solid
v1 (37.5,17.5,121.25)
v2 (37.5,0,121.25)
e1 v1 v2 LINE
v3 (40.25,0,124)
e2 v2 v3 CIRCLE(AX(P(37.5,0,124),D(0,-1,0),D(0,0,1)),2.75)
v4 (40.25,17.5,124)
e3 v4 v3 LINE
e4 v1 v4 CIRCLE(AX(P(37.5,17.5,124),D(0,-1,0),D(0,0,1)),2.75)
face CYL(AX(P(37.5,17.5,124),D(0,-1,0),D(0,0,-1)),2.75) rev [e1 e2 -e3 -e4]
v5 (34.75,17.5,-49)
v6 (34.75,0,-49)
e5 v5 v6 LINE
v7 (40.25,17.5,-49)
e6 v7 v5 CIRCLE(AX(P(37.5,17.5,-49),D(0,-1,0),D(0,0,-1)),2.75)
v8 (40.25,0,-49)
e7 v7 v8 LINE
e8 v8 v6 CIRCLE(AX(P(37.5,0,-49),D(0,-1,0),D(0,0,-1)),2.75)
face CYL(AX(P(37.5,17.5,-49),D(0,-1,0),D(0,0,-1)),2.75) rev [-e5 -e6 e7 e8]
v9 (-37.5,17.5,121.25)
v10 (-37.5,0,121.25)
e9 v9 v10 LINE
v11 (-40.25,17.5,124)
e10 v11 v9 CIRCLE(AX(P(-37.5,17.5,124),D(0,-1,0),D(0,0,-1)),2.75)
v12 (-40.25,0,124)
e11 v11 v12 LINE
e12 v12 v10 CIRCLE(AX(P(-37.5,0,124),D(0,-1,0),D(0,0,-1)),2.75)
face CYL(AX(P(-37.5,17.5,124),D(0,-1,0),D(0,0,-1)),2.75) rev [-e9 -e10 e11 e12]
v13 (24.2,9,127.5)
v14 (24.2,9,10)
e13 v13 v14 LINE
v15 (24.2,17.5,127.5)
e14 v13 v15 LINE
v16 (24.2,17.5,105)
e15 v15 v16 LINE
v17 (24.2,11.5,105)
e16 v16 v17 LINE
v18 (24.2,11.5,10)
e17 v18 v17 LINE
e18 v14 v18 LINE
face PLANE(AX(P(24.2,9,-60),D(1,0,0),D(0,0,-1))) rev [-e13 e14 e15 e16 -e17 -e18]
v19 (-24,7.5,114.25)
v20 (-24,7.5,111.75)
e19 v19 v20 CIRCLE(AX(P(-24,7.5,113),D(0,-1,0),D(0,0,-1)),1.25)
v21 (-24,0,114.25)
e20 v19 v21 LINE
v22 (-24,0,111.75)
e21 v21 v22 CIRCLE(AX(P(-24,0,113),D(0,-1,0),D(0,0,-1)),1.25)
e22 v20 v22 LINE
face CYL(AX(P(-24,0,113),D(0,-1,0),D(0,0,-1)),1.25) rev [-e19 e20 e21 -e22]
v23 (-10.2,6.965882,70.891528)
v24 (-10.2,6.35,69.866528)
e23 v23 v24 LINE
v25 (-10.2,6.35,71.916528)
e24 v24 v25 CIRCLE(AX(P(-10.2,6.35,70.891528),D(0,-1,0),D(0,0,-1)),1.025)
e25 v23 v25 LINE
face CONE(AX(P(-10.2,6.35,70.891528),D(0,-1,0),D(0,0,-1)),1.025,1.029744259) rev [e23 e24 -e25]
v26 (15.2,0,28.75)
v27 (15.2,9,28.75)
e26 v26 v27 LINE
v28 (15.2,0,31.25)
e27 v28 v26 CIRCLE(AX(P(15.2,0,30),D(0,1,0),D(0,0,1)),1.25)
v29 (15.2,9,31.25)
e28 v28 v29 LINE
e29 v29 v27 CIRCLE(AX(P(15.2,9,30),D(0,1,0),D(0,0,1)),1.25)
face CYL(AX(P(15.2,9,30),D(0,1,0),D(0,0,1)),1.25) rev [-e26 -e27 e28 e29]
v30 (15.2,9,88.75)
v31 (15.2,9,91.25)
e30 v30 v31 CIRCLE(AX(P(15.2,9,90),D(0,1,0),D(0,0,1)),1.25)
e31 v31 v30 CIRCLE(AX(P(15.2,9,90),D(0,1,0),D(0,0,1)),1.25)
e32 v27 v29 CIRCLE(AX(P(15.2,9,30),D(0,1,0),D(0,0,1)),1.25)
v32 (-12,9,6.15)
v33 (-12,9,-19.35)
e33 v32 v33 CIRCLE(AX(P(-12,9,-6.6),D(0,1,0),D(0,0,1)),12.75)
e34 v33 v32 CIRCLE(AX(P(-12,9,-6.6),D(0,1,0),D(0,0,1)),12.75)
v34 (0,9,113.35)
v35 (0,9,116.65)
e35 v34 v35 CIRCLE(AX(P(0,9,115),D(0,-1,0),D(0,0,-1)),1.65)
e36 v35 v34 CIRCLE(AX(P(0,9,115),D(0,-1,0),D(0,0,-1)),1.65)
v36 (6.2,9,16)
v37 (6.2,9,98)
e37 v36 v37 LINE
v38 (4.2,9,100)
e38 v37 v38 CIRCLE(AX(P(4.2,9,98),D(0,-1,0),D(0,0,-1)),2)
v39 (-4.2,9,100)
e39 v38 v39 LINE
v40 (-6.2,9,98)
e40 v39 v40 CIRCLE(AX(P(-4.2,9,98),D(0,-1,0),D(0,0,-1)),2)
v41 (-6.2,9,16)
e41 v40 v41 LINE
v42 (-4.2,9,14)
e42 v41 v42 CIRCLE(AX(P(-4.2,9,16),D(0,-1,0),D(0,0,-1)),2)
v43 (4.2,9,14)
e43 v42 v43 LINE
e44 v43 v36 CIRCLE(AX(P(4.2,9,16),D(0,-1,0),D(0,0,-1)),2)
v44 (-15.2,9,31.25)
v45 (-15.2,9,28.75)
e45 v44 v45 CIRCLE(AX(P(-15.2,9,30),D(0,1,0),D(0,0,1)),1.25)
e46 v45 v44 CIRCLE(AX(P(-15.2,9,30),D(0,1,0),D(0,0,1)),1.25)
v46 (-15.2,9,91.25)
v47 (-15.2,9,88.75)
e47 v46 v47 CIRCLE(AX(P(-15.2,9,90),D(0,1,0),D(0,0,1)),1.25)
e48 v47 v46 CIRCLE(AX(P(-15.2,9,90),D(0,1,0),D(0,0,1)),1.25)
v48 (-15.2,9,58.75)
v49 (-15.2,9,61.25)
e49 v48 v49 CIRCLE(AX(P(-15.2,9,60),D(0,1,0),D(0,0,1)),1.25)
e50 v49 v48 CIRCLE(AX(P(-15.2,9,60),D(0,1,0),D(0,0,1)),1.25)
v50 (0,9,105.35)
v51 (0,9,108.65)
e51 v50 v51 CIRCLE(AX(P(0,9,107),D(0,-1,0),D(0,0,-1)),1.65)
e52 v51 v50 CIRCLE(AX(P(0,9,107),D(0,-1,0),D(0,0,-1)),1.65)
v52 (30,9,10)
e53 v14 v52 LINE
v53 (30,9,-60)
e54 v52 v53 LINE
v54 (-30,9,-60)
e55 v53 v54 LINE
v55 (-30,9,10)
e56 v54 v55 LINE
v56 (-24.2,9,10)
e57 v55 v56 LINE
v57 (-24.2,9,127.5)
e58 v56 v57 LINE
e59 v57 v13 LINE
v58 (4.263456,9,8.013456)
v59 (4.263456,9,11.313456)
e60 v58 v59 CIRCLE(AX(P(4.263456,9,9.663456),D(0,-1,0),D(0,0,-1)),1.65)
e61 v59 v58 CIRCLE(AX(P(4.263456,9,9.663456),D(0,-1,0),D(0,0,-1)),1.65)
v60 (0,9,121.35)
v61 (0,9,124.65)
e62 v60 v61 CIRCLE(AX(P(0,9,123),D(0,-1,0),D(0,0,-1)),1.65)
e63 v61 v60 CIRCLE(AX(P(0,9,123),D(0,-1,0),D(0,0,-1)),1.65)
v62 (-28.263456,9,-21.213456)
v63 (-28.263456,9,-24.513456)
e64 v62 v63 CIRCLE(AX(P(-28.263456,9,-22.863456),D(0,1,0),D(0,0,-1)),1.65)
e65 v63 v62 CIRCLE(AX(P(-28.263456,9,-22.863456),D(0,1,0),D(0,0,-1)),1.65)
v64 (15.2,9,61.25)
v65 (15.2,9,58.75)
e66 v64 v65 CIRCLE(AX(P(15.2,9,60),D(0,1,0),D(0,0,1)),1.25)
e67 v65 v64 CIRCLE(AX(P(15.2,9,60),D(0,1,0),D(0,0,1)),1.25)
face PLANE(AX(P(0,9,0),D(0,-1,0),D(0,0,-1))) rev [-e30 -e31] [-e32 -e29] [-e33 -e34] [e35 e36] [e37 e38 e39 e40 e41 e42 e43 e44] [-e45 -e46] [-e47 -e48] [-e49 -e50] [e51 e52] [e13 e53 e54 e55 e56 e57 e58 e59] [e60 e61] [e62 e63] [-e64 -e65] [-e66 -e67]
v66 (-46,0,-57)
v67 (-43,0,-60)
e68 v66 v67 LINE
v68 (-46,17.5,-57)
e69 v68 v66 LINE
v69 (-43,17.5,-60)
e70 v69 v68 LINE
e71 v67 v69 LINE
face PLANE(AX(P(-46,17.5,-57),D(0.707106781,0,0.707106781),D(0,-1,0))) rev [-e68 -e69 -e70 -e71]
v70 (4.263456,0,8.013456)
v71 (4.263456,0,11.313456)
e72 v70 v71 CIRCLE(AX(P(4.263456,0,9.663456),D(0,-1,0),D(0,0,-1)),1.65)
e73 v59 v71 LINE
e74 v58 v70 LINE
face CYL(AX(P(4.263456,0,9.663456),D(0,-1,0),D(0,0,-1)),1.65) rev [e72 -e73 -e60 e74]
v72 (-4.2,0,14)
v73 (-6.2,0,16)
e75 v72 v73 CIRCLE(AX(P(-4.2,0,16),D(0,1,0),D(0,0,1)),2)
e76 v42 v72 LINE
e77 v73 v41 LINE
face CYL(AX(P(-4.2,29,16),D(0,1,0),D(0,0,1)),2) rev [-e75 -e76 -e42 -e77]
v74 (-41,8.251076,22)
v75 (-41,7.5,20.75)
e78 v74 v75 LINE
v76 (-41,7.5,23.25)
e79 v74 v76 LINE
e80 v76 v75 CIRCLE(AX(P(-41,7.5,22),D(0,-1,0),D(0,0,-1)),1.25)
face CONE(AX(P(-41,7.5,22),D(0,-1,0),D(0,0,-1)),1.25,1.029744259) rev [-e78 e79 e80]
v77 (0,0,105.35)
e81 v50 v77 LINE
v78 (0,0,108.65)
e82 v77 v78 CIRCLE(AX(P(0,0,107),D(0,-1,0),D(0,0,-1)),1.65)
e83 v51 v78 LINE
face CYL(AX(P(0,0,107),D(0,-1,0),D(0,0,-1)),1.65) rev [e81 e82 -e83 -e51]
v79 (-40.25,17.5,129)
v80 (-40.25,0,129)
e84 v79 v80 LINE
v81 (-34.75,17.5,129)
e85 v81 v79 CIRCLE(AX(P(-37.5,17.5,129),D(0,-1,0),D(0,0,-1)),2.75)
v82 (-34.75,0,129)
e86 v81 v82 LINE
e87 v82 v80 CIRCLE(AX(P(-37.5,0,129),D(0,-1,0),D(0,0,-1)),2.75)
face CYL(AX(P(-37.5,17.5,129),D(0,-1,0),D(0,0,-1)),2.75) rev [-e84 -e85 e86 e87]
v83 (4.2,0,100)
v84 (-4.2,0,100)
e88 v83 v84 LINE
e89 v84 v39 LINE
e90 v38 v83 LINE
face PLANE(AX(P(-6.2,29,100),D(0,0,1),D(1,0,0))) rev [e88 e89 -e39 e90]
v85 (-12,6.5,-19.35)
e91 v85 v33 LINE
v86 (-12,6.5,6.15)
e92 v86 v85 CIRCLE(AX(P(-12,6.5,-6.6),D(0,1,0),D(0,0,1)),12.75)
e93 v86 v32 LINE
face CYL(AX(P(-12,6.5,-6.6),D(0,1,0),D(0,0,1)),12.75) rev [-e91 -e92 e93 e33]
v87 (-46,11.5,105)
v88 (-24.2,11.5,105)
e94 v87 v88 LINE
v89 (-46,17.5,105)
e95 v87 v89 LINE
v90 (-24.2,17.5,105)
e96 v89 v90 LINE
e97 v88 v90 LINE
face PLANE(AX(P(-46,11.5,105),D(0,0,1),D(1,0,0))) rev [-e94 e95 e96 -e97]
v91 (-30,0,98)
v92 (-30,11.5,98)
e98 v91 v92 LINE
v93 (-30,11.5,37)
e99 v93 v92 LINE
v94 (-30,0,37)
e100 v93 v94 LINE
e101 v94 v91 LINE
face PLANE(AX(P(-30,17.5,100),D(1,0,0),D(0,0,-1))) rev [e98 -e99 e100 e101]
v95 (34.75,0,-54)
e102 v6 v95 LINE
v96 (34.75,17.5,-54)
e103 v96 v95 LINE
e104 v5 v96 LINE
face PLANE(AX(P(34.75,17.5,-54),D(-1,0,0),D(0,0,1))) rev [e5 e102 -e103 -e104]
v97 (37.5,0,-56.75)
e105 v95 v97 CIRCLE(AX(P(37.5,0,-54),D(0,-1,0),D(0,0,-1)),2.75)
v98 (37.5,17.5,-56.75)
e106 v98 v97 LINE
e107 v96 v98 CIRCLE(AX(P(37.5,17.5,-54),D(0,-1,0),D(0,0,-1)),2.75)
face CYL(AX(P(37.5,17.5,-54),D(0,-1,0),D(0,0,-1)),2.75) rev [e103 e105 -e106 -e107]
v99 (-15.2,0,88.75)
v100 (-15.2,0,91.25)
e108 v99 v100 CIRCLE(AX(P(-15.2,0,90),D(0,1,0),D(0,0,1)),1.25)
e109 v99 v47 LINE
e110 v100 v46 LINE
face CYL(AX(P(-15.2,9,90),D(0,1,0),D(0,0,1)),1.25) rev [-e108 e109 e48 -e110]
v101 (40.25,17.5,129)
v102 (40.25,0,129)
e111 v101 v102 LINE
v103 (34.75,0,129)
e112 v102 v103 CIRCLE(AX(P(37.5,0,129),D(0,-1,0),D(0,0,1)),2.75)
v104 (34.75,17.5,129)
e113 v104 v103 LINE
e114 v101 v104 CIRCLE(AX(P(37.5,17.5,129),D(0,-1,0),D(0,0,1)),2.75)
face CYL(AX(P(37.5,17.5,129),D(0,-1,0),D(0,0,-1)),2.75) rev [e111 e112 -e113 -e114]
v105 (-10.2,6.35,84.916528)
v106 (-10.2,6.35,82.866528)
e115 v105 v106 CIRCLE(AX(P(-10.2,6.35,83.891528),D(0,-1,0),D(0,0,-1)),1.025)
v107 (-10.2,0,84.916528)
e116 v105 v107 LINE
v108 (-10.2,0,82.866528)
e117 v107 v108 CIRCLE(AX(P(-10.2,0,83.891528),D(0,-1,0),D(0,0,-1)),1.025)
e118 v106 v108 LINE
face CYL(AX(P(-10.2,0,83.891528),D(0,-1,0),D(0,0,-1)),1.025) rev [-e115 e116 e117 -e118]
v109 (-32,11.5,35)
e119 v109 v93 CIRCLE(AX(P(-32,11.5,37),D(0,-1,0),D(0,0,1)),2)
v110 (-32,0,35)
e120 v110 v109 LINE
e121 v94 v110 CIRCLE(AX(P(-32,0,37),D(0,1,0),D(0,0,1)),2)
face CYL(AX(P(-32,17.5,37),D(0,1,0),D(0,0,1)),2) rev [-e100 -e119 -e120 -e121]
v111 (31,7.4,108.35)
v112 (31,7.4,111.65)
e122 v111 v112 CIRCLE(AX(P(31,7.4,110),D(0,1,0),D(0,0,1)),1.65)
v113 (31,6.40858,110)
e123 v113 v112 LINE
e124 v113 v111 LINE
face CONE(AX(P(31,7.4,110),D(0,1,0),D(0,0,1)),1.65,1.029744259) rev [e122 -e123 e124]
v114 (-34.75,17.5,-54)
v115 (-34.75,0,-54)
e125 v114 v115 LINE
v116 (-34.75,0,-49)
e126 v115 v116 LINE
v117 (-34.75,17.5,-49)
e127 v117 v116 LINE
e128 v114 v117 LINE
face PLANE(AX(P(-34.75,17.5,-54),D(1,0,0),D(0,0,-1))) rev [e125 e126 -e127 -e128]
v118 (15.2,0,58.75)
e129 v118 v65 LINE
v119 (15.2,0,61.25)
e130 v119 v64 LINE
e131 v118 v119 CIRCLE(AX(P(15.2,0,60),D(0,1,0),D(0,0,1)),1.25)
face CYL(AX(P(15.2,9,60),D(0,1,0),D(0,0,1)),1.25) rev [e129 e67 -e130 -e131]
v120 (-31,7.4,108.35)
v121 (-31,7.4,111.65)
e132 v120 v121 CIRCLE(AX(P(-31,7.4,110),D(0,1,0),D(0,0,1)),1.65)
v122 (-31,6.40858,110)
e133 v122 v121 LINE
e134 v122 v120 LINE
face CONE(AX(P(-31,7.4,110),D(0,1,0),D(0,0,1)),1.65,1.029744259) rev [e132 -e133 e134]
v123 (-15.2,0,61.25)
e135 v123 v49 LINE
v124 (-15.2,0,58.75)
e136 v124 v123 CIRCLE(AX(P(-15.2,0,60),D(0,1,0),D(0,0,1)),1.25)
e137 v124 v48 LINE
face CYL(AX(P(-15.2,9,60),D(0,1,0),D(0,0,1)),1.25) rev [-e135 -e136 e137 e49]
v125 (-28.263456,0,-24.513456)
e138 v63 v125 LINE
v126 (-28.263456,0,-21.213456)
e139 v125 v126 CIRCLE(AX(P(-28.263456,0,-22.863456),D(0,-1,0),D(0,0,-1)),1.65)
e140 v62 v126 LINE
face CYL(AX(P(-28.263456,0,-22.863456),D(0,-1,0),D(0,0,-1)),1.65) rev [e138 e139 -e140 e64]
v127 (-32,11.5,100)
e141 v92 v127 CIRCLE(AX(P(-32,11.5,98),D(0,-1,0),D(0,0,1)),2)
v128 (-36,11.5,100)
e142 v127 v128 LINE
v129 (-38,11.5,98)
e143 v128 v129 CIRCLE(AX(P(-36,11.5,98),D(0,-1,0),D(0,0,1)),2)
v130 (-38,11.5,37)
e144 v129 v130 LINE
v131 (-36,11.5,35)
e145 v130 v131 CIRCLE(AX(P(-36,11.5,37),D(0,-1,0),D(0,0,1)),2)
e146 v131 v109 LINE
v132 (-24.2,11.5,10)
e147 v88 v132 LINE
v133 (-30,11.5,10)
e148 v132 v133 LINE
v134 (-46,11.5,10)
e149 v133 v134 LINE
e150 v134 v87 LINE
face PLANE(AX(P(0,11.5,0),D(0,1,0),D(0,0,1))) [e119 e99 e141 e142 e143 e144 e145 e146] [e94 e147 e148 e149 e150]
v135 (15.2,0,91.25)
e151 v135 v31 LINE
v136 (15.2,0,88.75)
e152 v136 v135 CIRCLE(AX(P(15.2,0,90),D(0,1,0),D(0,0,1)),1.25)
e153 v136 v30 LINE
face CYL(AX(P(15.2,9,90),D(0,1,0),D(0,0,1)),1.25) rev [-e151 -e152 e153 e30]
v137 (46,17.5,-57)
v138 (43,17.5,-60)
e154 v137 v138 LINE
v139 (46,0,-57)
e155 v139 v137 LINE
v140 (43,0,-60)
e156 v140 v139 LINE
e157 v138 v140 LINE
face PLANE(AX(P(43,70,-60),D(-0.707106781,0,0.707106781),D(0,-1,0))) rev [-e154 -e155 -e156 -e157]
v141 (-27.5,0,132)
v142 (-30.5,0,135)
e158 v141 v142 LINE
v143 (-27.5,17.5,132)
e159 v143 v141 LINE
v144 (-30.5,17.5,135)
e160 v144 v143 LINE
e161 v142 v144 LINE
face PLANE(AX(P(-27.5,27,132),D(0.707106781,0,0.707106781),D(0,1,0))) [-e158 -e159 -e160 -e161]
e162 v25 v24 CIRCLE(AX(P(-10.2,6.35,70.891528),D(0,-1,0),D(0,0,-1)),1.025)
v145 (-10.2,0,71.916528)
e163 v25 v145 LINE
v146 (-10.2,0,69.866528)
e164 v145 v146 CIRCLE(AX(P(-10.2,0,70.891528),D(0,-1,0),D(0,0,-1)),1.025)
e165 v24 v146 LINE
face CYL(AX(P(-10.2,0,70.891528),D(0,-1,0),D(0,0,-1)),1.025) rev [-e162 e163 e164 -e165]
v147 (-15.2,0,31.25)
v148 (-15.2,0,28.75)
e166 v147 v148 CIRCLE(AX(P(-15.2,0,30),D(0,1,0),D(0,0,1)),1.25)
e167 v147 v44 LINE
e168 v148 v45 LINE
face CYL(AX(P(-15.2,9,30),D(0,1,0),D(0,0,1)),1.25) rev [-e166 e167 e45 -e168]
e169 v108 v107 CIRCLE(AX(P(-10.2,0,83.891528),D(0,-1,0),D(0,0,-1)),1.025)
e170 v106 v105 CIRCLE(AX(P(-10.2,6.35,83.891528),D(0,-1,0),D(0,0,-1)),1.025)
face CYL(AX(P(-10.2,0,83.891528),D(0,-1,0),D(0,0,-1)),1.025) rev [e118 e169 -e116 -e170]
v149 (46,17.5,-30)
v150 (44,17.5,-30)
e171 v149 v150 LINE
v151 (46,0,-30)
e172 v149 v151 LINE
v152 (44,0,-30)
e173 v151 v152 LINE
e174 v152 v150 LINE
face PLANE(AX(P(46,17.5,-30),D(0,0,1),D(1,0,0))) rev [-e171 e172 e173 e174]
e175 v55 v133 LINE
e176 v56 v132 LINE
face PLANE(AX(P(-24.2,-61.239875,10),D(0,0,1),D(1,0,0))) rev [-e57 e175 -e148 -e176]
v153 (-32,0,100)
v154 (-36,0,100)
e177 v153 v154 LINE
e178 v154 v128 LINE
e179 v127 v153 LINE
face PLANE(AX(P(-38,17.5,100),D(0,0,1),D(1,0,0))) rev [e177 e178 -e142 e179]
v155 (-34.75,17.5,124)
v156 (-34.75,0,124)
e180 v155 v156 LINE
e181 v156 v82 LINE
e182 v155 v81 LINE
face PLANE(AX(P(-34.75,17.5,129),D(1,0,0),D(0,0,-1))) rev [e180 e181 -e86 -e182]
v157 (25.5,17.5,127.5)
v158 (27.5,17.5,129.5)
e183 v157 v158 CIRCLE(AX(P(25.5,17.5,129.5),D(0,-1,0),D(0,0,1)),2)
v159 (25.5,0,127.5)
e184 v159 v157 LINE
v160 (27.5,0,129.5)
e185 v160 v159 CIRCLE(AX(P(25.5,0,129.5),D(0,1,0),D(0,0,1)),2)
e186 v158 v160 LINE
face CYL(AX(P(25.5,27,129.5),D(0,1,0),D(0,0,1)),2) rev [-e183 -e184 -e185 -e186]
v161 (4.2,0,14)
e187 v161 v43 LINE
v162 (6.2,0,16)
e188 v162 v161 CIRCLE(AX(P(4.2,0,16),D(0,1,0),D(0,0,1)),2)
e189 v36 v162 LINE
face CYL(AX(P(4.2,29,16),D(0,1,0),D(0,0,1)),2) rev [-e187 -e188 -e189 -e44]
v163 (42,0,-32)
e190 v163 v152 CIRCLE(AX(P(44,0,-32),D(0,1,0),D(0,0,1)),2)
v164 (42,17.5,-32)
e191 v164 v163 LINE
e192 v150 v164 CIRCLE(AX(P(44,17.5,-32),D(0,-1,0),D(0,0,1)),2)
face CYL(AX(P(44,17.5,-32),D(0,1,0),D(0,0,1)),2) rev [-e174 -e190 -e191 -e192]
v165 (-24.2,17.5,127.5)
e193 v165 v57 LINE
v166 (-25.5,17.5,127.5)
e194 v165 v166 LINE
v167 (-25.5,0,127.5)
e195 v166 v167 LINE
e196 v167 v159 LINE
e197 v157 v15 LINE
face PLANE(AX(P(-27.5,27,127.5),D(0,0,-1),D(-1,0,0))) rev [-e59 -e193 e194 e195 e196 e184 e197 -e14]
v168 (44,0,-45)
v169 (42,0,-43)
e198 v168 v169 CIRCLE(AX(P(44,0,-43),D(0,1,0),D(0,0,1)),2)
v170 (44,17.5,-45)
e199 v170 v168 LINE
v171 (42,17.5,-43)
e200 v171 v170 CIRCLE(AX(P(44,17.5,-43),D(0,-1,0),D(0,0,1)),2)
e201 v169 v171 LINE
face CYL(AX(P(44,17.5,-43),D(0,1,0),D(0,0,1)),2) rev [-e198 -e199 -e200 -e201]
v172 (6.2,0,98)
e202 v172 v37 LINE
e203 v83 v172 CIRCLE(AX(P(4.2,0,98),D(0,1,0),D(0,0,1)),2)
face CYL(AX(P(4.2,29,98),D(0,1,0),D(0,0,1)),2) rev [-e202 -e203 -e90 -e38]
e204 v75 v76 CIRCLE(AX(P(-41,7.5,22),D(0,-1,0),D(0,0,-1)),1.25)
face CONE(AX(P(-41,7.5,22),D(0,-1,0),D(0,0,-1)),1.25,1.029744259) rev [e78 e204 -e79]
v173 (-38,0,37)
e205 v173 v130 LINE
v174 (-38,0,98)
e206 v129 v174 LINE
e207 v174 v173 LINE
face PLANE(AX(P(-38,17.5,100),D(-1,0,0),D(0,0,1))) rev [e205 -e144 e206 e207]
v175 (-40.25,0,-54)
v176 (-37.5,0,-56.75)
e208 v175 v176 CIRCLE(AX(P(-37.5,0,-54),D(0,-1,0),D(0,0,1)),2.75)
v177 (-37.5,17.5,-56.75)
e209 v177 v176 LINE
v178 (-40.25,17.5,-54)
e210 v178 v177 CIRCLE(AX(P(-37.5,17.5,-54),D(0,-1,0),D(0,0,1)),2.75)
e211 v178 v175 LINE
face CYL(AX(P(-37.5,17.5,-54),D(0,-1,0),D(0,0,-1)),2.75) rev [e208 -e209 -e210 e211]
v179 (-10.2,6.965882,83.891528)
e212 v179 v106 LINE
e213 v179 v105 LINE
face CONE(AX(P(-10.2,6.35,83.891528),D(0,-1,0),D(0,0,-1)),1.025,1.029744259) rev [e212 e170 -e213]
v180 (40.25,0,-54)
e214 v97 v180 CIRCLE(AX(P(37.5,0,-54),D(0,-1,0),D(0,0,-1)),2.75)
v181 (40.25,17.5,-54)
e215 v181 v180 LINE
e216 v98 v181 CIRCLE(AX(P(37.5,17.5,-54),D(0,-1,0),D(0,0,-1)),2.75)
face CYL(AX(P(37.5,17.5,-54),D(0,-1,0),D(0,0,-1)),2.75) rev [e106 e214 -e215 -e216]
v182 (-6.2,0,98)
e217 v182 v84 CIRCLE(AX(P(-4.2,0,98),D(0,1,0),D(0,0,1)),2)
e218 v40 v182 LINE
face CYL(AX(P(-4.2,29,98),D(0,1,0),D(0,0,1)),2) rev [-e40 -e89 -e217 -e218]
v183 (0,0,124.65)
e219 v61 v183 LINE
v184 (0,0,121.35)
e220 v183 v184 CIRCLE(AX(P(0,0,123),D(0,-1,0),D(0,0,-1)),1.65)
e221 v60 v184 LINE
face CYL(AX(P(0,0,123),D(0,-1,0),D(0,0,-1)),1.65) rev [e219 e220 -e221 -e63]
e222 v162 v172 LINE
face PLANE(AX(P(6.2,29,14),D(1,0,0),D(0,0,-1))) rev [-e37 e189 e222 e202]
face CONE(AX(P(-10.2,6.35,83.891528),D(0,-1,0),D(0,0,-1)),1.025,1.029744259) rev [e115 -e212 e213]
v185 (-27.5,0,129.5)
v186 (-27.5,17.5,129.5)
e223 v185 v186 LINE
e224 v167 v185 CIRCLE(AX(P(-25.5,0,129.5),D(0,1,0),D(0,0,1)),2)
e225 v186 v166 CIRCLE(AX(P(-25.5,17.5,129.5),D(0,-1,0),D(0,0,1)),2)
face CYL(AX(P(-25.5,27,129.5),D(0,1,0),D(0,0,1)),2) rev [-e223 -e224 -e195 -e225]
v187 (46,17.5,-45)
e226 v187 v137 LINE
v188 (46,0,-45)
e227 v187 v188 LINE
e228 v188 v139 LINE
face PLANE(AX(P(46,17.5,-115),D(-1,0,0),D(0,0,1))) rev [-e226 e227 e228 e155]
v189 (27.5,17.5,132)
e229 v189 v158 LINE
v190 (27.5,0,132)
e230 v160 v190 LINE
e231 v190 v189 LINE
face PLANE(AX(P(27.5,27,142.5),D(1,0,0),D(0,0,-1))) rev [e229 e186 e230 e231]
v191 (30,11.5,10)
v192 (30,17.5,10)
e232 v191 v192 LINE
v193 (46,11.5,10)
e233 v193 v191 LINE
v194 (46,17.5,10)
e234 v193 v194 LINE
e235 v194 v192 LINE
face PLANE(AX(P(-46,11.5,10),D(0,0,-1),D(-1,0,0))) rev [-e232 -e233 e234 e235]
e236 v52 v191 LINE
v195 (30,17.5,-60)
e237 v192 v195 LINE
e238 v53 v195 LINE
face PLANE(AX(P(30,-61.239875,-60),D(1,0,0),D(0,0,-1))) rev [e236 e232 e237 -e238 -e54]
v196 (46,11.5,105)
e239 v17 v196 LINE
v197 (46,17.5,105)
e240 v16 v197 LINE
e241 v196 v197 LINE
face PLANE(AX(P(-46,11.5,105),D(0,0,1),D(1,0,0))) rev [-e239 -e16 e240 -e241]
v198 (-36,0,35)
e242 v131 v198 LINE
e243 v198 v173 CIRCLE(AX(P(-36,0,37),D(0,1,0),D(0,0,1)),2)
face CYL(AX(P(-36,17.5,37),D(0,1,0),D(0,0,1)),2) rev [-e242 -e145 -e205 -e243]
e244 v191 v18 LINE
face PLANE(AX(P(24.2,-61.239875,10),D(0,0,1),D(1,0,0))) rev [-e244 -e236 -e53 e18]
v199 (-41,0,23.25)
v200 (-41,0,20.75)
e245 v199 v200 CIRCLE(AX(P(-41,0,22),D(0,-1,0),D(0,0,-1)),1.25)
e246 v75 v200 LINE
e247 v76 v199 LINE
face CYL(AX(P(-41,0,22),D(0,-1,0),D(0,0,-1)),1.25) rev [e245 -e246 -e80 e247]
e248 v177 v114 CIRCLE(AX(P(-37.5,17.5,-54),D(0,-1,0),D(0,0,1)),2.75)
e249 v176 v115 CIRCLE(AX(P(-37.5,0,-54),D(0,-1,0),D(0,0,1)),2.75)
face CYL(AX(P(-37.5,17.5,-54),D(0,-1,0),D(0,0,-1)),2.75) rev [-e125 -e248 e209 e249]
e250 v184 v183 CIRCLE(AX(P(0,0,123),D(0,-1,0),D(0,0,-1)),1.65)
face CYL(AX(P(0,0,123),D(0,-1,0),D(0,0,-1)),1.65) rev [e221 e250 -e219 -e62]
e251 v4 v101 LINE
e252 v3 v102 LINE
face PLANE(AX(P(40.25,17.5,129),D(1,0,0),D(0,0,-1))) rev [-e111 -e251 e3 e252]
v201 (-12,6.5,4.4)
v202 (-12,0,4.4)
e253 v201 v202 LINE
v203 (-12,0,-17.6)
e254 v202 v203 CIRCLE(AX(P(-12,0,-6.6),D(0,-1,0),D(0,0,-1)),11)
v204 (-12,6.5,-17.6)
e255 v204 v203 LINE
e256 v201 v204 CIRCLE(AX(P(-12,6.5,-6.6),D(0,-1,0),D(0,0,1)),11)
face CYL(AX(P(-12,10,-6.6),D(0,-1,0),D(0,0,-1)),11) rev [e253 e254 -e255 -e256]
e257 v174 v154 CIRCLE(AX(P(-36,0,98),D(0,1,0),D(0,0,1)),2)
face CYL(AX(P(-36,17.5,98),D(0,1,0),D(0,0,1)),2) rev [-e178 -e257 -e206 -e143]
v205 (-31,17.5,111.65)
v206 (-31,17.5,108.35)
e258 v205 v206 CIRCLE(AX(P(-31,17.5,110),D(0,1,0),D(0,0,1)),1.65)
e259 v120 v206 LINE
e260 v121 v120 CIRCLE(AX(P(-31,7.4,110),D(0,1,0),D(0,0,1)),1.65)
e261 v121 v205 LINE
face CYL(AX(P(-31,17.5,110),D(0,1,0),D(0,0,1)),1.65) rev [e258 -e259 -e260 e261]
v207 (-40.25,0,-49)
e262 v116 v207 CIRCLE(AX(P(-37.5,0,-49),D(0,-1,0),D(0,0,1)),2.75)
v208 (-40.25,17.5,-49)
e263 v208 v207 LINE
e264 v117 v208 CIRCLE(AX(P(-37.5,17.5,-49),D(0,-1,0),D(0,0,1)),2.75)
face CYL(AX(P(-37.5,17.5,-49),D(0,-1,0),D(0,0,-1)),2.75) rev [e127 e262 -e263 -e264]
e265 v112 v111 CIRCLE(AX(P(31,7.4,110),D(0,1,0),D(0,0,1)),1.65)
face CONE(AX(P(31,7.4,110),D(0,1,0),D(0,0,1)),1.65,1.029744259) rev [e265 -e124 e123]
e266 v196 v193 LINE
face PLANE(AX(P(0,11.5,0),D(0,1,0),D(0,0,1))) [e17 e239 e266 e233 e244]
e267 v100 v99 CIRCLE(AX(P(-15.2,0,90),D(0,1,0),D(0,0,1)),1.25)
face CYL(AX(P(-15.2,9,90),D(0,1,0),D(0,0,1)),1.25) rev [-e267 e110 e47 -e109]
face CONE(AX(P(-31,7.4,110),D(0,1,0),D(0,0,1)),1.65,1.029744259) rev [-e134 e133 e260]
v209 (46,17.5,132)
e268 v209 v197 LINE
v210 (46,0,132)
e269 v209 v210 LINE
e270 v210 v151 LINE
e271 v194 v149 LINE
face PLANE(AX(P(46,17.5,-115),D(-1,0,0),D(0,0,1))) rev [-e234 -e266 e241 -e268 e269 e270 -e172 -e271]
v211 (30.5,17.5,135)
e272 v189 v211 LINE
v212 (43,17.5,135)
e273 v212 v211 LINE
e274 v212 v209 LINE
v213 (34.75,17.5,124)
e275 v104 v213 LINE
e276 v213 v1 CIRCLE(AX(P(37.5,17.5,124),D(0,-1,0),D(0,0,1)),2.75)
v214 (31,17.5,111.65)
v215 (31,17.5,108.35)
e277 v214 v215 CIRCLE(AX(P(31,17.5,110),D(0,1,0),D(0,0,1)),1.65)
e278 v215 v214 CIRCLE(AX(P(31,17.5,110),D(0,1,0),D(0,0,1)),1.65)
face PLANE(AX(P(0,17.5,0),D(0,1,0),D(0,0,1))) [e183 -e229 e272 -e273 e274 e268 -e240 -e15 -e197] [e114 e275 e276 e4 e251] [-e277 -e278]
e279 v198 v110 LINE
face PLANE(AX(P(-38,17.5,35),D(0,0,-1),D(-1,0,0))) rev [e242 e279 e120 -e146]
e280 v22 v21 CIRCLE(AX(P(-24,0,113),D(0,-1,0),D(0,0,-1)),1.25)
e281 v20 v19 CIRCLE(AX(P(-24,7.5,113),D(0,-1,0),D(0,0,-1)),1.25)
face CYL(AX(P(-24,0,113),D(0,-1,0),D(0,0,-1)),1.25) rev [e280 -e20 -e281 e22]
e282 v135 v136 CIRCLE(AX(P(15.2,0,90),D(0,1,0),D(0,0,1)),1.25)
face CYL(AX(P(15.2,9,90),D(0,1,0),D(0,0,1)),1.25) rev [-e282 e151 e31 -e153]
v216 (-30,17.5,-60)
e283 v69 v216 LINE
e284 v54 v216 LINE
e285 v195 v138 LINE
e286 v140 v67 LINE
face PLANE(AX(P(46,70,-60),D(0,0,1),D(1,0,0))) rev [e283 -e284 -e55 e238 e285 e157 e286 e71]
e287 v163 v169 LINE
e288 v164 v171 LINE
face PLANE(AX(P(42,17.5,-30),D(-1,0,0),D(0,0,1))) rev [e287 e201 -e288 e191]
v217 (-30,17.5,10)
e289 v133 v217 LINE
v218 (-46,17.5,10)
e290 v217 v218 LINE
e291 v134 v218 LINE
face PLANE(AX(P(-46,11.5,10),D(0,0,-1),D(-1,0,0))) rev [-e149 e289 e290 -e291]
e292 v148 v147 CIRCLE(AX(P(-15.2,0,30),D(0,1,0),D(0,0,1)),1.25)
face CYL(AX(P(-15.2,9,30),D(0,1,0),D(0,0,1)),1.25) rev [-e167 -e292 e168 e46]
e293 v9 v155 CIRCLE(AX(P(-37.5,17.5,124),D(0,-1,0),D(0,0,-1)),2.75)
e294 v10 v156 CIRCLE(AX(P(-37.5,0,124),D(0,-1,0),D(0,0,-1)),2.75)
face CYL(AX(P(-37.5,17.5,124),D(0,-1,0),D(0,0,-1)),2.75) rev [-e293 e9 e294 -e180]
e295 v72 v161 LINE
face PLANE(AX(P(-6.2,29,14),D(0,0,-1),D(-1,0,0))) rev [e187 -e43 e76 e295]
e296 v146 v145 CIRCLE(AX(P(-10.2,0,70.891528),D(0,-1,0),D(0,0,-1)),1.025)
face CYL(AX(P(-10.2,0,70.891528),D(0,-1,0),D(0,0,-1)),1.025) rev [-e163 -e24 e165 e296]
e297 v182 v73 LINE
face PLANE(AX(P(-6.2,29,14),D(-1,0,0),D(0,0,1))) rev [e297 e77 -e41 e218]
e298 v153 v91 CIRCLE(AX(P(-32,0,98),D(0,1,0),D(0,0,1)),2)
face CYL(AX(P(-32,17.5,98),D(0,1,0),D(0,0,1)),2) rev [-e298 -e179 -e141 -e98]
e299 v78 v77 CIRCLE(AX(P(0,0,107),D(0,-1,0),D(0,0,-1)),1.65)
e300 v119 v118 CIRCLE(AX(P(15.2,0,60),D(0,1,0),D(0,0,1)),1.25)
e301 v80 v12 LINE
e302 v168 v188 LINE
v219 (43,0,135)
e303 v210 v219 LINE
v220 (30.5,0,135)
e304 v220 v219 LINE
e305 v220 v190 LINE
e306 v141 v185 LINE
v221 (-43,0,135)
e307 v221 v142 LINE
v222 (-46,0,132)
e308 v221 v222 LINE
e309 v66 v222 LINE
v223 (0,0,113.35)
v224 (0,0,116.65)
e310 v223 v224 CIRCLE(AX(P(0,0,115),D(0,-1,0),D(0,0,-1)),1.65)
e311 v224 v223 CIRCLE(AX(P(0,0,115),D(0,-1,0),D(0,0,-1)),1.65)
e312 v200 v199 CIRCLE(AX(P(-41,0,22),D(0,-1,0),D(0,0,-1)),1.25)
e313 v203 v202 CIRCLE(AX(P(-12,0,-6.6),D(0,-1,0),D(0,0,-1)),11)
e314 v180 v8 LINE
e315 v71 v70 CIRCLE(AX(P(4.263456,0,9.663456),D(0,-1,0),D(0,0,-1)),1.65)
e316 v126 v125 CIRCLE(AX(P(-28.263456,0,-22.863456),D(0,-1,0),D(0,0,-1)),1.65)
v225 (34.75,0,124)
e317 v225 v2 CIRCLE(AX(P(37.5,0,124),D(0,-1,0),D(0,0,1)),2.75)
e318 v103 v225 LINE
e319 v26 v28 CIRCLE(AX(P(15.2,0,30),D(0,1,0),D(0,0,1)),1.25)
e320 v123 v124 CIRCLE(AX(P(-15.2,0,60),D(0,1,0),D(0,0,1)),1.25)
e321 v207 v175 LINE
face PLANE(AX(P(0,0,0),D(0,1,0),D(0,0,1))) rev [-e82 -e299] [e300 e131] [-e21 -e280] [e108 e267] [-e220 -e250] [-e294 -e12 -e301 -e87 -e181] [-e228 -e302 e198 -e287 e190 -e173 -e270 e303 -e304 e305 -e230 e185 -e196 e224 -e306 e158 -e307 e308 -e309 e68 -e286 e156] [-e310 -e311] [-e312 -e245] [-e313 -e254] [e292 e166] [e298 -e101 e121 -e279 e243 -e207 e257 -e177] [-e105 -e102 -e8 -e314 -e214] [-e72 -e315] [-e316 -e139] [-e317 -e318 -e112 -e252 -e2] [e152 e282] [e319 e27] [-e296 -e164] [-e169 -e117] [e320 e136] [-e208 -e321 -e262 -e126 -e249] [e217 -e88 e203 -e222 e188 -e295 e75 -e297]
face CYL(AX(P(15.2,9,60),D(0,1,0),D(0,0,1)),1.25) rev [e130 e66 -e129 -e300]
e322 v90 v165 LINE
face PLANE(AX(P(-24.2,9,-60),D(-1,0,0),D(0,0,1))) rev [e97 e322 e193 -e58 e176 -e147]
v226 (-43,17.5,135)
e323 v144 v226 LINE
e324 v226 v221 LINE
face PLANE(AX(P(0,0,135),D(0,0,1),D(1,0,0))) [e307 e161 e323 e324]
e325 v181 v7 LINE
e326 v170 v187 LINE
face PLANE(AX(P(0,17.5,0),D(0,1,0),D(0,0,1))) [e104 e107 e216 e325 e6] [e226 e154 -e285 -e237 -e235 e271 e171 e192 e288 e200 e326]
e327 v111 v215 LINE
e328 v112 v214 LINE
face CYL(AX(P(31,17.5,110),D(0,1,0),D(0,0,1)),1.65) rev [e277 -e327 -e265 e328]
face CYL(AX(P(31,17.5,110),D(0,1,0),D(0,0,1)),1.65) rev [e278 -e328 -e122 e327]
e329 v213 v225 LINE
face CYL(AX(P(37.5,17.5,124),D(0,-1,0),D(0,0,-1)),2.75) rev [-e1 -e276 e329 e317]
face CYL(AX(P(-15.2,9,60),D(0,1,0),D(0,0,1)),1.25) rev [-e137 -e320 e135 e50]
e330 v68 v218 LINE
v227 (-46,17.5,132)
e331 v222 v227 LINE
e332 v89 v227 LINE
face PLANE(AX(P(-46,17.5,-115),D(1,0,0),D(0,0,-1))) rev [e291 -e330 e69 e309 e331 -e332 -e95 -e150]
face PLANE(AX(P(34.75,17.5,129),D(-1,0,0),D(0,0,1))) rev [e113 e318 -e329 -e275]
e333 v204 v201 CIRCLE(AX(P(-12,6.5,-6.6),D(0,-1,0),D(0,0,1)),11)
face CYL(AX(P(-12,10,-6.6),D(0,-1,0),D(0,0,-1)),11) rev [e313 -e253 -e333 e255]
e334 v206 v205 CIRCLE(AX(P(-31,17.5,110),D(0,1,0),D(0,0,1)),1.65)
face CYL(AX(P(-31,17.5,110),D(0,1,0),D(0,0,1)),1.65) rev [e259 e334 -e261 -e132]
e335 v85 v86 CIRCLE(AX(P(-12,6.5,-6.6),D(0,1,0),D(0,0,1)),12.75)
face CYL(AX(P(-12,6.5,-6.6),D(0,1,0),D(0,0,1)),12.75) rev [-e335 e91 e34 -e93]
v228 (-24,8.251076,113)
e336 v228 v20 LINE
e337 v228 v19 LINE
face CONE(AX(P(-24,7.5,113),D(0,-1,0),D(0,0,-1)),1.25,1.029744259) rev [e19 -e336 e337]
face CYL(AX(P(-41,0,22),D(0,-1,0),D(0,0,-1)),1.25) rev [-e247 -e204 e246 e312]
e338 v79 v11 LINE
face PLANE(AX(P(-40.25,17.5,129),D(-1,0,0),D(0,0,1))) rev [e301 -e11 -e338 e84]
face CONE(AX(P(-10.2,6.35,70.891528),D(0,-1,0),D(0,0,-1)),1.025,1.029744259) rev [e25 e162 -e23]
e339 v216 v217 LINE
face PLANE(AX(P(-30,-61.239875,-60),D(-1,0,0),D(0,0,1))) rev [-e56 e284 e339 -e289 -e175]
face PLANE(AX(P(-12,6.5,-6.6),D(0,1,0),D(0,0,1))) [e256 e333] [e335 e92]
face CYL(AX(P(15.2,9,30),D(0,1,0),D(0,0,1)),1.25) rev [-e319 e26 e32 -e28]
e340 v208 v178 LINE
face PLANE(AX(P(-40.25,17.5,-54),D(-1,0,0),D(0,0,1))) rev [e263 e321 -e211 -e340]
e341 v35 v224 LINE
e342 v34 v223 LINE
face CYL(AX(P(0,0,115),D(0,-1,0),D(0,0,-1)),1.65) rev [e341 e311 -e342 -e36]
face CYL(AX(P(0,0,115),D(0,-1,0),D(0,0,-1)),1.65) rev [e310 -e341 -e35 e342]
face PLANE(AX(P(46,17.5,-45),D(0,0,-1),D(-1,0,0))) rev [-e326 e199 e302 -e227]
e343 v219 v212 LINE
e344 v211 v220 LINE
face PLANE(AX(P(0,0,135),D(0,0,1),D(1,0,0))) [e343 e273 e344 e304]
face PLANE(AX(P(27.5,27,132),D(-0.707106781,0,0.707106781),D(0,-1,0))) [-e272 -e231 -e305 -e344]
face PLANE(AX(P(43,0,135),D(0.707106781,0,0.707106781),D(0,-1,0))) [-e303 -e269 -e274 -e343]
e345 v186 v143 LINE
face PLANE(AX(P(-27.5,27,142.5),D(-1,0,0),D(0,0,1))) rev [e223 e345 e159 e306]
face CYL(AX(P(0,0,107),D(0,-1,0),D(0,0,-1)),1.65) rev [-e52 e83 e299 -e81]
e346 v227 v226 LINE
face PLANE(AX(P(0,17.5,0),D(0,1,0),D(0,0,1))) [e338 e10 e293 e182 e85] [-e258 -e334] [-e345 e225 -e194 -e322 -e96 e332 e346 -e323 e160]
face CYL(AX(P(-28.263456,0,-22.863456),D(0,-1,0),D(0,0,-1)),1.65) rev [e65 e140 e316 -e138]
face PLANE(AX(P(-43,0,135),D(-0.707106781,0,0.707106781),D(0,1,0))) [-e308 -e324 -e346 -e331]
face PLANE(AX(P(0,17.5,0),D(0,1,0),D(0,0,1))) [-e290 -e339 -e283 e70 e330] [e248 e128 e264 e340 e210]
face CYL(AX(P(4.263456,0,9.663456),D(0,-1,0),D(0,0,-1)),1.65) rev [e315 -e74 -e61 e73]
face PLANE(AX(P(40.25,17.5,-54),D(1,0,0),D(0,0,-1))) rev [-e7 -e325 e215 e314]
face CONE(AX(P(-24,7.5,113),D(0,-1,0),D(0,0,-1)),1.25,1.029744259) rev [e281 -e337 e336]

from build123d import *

# Parameters (mm, degrees)
SKETCH1_W               = 92
SKETCH1_H               = 230
BOSS_EXTRUDE1_DEPTH     = 17.5
SKETCH3_W               = 92
SKETCH3_H               = 20
CUT_EXTRUDE2_DEPTH      = 57
SKETCH7_W               = 92
SKETCH7_H               = 35
CUT_EXTRUDE5_DEPTH      = 70
SKETCH6_W               = 48.4
SKETCH6_H               = 175
CUT_EXTRUDE4_DEPTH      = 8.5
M3_TAPPED_HOLE1_D       = 2.5
SKETCH4_W               = 12.4
SKETCH4_H               = 86
CUT_EXTRUDE3_DEPTH      = 29
CHAMFER1_SIZE           = 3
FILLET1_R               = 2
SKETCH2_R               = 11
CUT_EXTRUDE1_DEPTH      = 10
BOSS_EXTRUDE2_DEPTH     = 20
CUT_EXTRUDE9_DEPTH      = 144.69150984
CHAMFER2_SIZE           = 3
SKETCH22_W              = 8
SKETCH22_H              = 65
CUT_EXTRUDE10_DEPTH     = 144.69150984
FILLET2_R               = 2
SKETCH12_R              = 12.75
CUT_EXTRUDE7_DEPTH      = 2.5
SKETCH23_W              = 92
SKETCH23_H              = 95
CUT_EXTRUDE11_DEPTH     = 6
M2_5_TAPPED_HOLE1_D     = 2.05
M2_5_TAPPED_HOLE1_DEPTH = 6.35
M2_5_TAPPED_HOLE1_TIP   = 0.615882135
M4_TAPPED_HOLE4_D       = 3.3
M4_TAPPED_HOLE4_DEPTH   = 10.1
M4_TAPPED_HOLE4_TIP     = 0.991420021
SKETCH16_R              = 1
CUT_EXTRUDE8_DEPTH      = 10
SKETCH30_W              = 4
SKETCH30_H              = 15
CUT_EXTRUDE12_DEPTH     = 144.69150984
M4_TAPPED_HOLE2_D       = 3.3
FILLET3_R               = 2
LPATTERN1_COUNT         = 3
LPATTERN1_PITCH         = 8
SKETCH31_W              = 55
SKETCH31_H              = 15
CUT_EXTRUDE13_DEPTH     = 27
FILLET4_R               = 2
CHAMFER3_SIZE           = 3
CUT_EXTRUDE14_REACH     = 145.692
SKETCH32_W              = 5.8
SKETCH32_H              = 70
M3_TAPPED_HOLE2_D       = 2.5
M3_TAPPED_HOLE2_DEPTH   = 7.5
M3_TAPPED_HOLE2_TIP     = 0.751075774
M3_TAPPED_HOLE3_D       = 2.5
M3_TAPPED_HOLE3_DEPTH   = 7.5
M3_TAPPED_HOLE3_TIP     = 0.751075774


with BuildPart() as part:
    # Sketch1 → Boss-Extrude1 (new body)
    with BuildSketch(Plane(origin=(0, 0, 0), x_dir=(1, 0, 0), z_dir=(0, 1, 0))):
        Rectangle(SKETCH1_W, SKETCH1_H)
    extrude(amount=BOSS_EXTRUDE1_DEPTH)

    # Sketch3 → Cut-Extrude2 (cut)
    with BuildSketch(Plane.XZ):
        with Locations((0, -105)):
            Rectangle(SKETCH3_W, SKETCH3_H)
    extrude(amount=-CUT_EXTRUDE2_DEPTH, mode=Mode.SUBTRACT)

    # Sketch7 → Cut-Extrude5 (cut)
    with BuildSketch(Plane.XZ):
        with Locations((0, -77.5)):
            Rectangle(SKETCH7_W, SKETCH7_H)
    extrude(amount=-CUT_EXTRUDE5_DEPTH, mode=Mode.SUBTRACT)

    # Sketch6 → Cut-Extrude4 (cut)
    with BuildSketch(Plane(origin=(0, 17.5, 0), x_dir=(1, 0, 0), z_dir=(0, 1, 0))):
        with Locations((0, -27.5)):
            Rectangle(SKETCH6_W, SKETCH6_H)
    extrude(amount=-CUT_EXTRUDE4_DEPTH, mode=Mode.SUBTRACT)

    # M3 Tapped Hole1 (through all)
    with Locations(Plane(origin=(0, 9, 0), x_dir=(1, 0, 0), z_dir=(0, 1, 0))):
        with Locations((15.2, -90), (-15.2, -90), (-15.2, -60), (15.2, -60), (15.2, -30), (-15.2, -30)):
            Hole(M3_TAPPED_HOLE1_D / 2)

    # Sketch4 → Cut-Extrude3 (cut)
    with BuildSketch(Plane.XZ):
        with Locations((0, 57)):
            Rectangle(SKETCH4_W, SKETCH4_H)
    extrude(amount=-CUT_EXTRUDE3_DEPTH, mode=Mode.SUBTRACT)

    # Chamfer1
    chamfer1_edges = [part.edges().sort_by_distance(p)[0] for p in [
        (46, 8.75, -60),
        (-46, 8.75, -60),
    ]]
    chamfer(chamfer1_edges, length=CHAMFER1_SIZE)

    # Fillet1
    fillet1_edges = [part.edges().sort_by_distance(p)[0] for p in [
        (6.2, 4.5, 100),
        (6.2, 4.5, 14),
        (-6.2, 4.5, 14),
        (-6.2, 4.5, 100),
    ]]
    fillet(fillet1_edges, radius=FILLET1_R)

    # Sketch2 → Cut-Extrude1 (cut)
    with BuildSketch(Plane.XZ):
        with Locations(Location((-12, -6.6, 0), (0, 0, 270))):
            Circle(SKETCH2_R)
    extrude(amount=-CUT_EXTRUDE1_DEPTH, mode=Mode.SUBTRACT)

    # Sketch20 → Boss-Extrude2 (add)
    with BuildSketch(Plane.XY.offset(115)):
        Polygon((-46, 17.5), (-24.2, 17.5), (-24.2, 9), (24.2, 9), (24.2, 17.5), (46, 17.5), (46, 0), (-46, 0), align=None)
    extrude(amount=BOSS_EXTRUDE2_DEPTH)

    # Sketch21 → Cut-Extrude9 (cut, through all)
    with BuildSketch(Plane.XZ):
        with BuildLine():
            Line((-34.75, 129), (-34.75, 124))
            ThreePointArc((-34.75, 124), (-37.5, 121.25), (-40.25, 124))
            Line((-40.25, 124), (-40.25, 129))
            ThreePointArc((-40.25, 129), (-37.5, 131.75), (-34.75, 129))
        make_face()
        with BuildLine():
            Line((34.75, 129), (34.75, 124))
            ThreePointArc((34.75, 124), (37.5, 121.25), (40.25, 124))
            Line((40.25, 124), (40.25, 129))
            ThreePointArc((40.25, 129), (37.5, 131.75), (34.75, 129))
        make_face()
        with BuildLine():
            Line((34.75, -54), (34.75, -49))
            ThreePointArc((34.75, -49), (37.5, -46.25), (40.25, -49))
            Line((40.25, -49), (40.25, -54))
            ThreePointArc((40.25, -54), (37.5, -56.75), (34.75, -54))
        make_face()
        with BuildLine():
            Line((-34.75, -54), (-34.75, -49))
            ThreePointArc((-34.75, -49), (-37.5, -46.25), (-40.25, -49))
            Line((-40.25, -49), (-40.25, -54))
            ThreePointArc((-40.25, -54), (-37.5, -56.75), (-34.75, -54))
        make_face()
    extrude(amount=-CUT_EXTRUDE9_DEPTH, mode=Mode.SUBTRACT)

    # Chamfer2
    chamfer2_edges = [part.edges().sort_by_distance(p)[0] for p in [
        (-46, 8.75, 135),
        (46, 8.75, 135),
    ]]
    chamfer(chamfer2_edges, length=CHAMFER2_SIZE)

    # Sketch22 → Cut-Extrude10 (cut, through all)
    with BuildSketch(Plane.XZ):
        with Locations((-34, 67.5)):
            Rectangle(SKETCH22_W, SKETCH22_H)
    extrude(amount=-CUT_EXTRUDE10_DEPTH, mode=Mode.SUBTRACT)

    # Fillet2
    fillet2_edges = [part.edges().sort_by_distance(p)[0] for p in [
        (-38, 8.75, 35),
        (-38, 8.75, 100),
        (-30, 8.75, 100),
        (-30, 8.75, 35),
    ]]
    fillet(fillet2_edges, radius=FILLET2_R)

    # Sketch12 → Cut-Extrude7 (cut)
    with BuildSketch(Plane(origin=(0, 9, 0), x_dir=(1, 0, 0), z_dir=(0, 1, 0))):
        with Locations(Location((-12, 6.6, 0), (0, 0, 270))):
            Circle(SKETCH12_R)
    extrude(amount=-CUT_EXTRUDE7_DEPTH, mode=Mode.SUBTRACT)

    # Sketch23 → Cut-Extrude11 (cut)
    with BuildSketch(Plane(origin=(0, 17.5, 0), x_dir=(1, 0, 0), z_dir=(0, 1, 0))):
        with Locations((0, -57.5)):
            Rectangle(SKETCH23_W, SKETCH23_H)
    extrude(amount=-CUT_EXTRUDE11_DEPTH, mode=Mode.SUBTRACT)

    # M2.5 Tapped Hole1
    with Locations(Plane(origin=(-10.2, 0, 83.891528236), x_dir=(0, 0, -1), z_dir=(0, -1, 0))):
        with Locations((0, 0), (13, 0)):
            Hole(M2_5_TAPPED_HOLE1_D / 2, depth=M2_5_TAPPED_HOLE1_DEPTH)
            with Locations((0, 0, -(M2_5_TAPPED_HOLE1_DEPTH + M2_5_TAPPED_HOLE1_TIP / 2))):  # 118° drill point
                Cone(0, M2_5_TAPPED_HOLE1_D / 2, M2_5_TAPPED_HOLE1_TIP, mode=Mode.SUBTRACT)

    # Sketch26 → M4 Tapped Hole3 (revolve, cut)
    with BuildSketch(Plane(origin=(0, 0, 107), x_dir=(0, 0, -1), z_dir=(1, 0, 0))):
        Polygon((0, 0), (0, 11.091420021), (1.65, 10.1), (1.65, 0), align=None)
    m4_tapped_hole3 = revolve(axis=Axis((0, -6.35, 107), (0, 1, 0)), mode=Mode.SUBTRACT)

    # M4 Tapped Hole4
    with Locations(Plane(origin=(0, 17.5, 0), x_dir=(1, 0, 0), z_dir=(0, 1, 0))):
        with Locations((31, -110), (-31, -110)):
            Hole(M4_TAPPED_HOLE4_D / 2, depth=M4_TAPPED_HOLE4_DEPTH)
            with Locations((0, 0, -(M4_TAPPED_HOLE4_DEPTH + M4_TAPPED_HOLE4_TIP / 2))):  # 118° drill point
                Cone(0, M4_TAPPED_HOLE4_D / 2, M4_TAPPED_HOLE4_TIP, mode=Mode.SUBTRACT)

    # Sketch16 → Cut-Extrude8 (cut)
    with BuildSketch(Plane.XZ):
        with Locations(Location((4.263455967, 9.663455967, 0), (0, 0, 270))):
            Circle(SKETCH16_R)
        with Locations(Location((-28.263455967, -22.863455967, 0), (0, 0, 270))):
            Circle(SKETCH16_R)
    extrude(amount=-CUT_EXTRUDE8_DEPTH, mode=Mode.SUBTRACT)

    # Sketch30 → Cut-Extrude12 (cut, through all)
    with BuildSketch(Plane.XZ):
        with Locations((44, -37.5)):
            Rectangle(SKETCH30_W, SKETCH30_H)
    extrude(amount=-CUT_EXTRUDE12_DEPTH, mode=Mode.SUBTRACT)

    # M4 Tapped Hole2 (through all)
    with Locations(Plane(origin=(-28.263455967, 0, -22.863455967), x_dir=(0, 0, -1), z_dir=(0, -1, 0))):
        with Locations((0, 0), (-32.526911934, 32.526911934)):
            Hole(M4_TAPPED_HOLE2_D / 2)

    # Fillet3
    fillet3_edges = [part.edges().sort_by_distance(p)[0] for p in [
        (42, 8.75, -45),
        (42, 8.75, -30),
    ]]
    fillet(fillet3_edges, radius=FILLET3_R)

    # LPattern1: M4 Tapped Hole3 ×3
    with Locations(*[(0, 0, i * LPATTERN1_PITCH) for i in range(1, LPATTERN1_COUNT)]):
        add(m4_tapped_hole3, mode=Mode.SUBTRACT)

    # Sketch31 → Cut-Extrude13 (cut)
    with BuildSketch(Plane.XZ):
        with Locations((0, 135)):
            Rectangle(SKETCH31_W, SKETCH31_H)
    extrude(amount=-CUT_EXTRUDE13_DEPTH, mode=Mode.SUBTRACT)

    # Fillet4
    fillet4_edges = [part.edges().sort_by_distance(p)[0] for p in [
        (27.5, 8.75, 127.5),
        (-27.5, 8.75, 127.5),
    ]]
    fillet(fillet4_edges, radius=FILLET4_R)

    # Chamfer3
    chamfer3_edges = [part.edges().sort_by_distance(p)[0] for p in [
        (-27.5, 8.75, 135),
        (27.5, 8.75, 135),
    ]]
    chamfer(chamfer3_edges, length=CHAMFER3_SIZE)

    # Cut-Extrude14: up to this face of the body (flat: up to its plane)
    cut_extrude14_end = Plane(part.part.faces().sort_by_distance((-0.202555348, 9, -15.347138665))[0])
    # Sketch32 → Cut-Extrude14 (cut, up to the picked face)
    with BuildSketch(Plane(origin=(0, 17.5, 0), x_dir=(1, 0, 0), z_dir=(0, 1, 0)), mode=Mode.PRIVATE) as cut_extrude14_sk1:
        with Locations((-27.1, 25)):
            Rectangle(SKETCH32_W, SKETCH32_H)
    cut_extrude14_tool1 = split(extrude(cut_extrude14_sk1.sketch, amount=-CUT_EXTRUDE14_REACH, mode=Mode.PRIVATE), bisect_by=cut_extrude14_end, keep=Keep.BOTH, mode=Mode.PRIVATE)
    # Sketch32 → Cut-Extrude14 (cut, up to the picked face)
    with BuildSketch(Plane(origin=(0, 17.5, 0), x_dir=(1, 0, 0), z_dir=(0, 1, 0)), mode=Mode.PRIVATE) as cut_extrude14_sk2:
        with Locations((27.1, 25)):
            Rectangle(SKETCH32_W, SKETCH32_H)
    cut_extrude14_tool2 = split(extrude(cut_extrude14_sk2.sketch, amount=-CUT_EXTRUDE14_REACH, mode=Mode.PRIVATE), bisect_by=cut_extrude14_end, keep=Keep.BOTH, mode=Mode.PRIVATE)
    add(cut_extrude14_tool1.solids().sort_by(Axis((-27.1, 17.5, -25), (0, -1, 0)))[0], mode=Mode.SUBTRACT)
    add(cut_extrude14_tool2.solids().sort_by(Axis((27.1, 17.5, -25), (0, -1, 0)))[0], mode=Mode.SUBTRACT)

    # M3 Tapped Hole2
    with Locations(Plane(origin=(0, 0, 0), x_dir=(-1, 0, 0), z_dir=(0, -1, 0))):
        with Locations((41, -22)):
            Hole(M3_TAPPED_HOLE2_D / 2, depth=M3_TAPPED_HOLE2_DEPTH)
            with Locations((0, 0, -(M3_TAPPED_HOLE2_DEPTH + M3_TAPPED_HOLE2_TIP / 2))):  # 118° drill point
                Cone(0, M3_TAPPED_HOLE2_D / 2, M3_TAPPED_HOLE2_TIP, mode=Mode.SUBTRACT)

    # M3 Tapped Hole3
    with Locations(Plane(origin=(0, 0, 0), x_dir=(-1, 0, 0), z_dir=(0, -1, 0))):
        with Locations((24, -113)):
            Hole(M3_TAPPED_HOLE3_D / 2, depth=M3_TAPPED_HOLE3_DEPTH)
            with Locations((0, 0, -(M3_TAPPED_HOLE3_DEPTH + M3_TAPPED_HOLE3_TIP / 2))):  # 118° drill point
                Cone(0, M3_TAPPED_HOLE3_D / 2, M3_TAPPED_HOLE3_TIP, mode=Mode.SUBTRACT)


solid = part.part
